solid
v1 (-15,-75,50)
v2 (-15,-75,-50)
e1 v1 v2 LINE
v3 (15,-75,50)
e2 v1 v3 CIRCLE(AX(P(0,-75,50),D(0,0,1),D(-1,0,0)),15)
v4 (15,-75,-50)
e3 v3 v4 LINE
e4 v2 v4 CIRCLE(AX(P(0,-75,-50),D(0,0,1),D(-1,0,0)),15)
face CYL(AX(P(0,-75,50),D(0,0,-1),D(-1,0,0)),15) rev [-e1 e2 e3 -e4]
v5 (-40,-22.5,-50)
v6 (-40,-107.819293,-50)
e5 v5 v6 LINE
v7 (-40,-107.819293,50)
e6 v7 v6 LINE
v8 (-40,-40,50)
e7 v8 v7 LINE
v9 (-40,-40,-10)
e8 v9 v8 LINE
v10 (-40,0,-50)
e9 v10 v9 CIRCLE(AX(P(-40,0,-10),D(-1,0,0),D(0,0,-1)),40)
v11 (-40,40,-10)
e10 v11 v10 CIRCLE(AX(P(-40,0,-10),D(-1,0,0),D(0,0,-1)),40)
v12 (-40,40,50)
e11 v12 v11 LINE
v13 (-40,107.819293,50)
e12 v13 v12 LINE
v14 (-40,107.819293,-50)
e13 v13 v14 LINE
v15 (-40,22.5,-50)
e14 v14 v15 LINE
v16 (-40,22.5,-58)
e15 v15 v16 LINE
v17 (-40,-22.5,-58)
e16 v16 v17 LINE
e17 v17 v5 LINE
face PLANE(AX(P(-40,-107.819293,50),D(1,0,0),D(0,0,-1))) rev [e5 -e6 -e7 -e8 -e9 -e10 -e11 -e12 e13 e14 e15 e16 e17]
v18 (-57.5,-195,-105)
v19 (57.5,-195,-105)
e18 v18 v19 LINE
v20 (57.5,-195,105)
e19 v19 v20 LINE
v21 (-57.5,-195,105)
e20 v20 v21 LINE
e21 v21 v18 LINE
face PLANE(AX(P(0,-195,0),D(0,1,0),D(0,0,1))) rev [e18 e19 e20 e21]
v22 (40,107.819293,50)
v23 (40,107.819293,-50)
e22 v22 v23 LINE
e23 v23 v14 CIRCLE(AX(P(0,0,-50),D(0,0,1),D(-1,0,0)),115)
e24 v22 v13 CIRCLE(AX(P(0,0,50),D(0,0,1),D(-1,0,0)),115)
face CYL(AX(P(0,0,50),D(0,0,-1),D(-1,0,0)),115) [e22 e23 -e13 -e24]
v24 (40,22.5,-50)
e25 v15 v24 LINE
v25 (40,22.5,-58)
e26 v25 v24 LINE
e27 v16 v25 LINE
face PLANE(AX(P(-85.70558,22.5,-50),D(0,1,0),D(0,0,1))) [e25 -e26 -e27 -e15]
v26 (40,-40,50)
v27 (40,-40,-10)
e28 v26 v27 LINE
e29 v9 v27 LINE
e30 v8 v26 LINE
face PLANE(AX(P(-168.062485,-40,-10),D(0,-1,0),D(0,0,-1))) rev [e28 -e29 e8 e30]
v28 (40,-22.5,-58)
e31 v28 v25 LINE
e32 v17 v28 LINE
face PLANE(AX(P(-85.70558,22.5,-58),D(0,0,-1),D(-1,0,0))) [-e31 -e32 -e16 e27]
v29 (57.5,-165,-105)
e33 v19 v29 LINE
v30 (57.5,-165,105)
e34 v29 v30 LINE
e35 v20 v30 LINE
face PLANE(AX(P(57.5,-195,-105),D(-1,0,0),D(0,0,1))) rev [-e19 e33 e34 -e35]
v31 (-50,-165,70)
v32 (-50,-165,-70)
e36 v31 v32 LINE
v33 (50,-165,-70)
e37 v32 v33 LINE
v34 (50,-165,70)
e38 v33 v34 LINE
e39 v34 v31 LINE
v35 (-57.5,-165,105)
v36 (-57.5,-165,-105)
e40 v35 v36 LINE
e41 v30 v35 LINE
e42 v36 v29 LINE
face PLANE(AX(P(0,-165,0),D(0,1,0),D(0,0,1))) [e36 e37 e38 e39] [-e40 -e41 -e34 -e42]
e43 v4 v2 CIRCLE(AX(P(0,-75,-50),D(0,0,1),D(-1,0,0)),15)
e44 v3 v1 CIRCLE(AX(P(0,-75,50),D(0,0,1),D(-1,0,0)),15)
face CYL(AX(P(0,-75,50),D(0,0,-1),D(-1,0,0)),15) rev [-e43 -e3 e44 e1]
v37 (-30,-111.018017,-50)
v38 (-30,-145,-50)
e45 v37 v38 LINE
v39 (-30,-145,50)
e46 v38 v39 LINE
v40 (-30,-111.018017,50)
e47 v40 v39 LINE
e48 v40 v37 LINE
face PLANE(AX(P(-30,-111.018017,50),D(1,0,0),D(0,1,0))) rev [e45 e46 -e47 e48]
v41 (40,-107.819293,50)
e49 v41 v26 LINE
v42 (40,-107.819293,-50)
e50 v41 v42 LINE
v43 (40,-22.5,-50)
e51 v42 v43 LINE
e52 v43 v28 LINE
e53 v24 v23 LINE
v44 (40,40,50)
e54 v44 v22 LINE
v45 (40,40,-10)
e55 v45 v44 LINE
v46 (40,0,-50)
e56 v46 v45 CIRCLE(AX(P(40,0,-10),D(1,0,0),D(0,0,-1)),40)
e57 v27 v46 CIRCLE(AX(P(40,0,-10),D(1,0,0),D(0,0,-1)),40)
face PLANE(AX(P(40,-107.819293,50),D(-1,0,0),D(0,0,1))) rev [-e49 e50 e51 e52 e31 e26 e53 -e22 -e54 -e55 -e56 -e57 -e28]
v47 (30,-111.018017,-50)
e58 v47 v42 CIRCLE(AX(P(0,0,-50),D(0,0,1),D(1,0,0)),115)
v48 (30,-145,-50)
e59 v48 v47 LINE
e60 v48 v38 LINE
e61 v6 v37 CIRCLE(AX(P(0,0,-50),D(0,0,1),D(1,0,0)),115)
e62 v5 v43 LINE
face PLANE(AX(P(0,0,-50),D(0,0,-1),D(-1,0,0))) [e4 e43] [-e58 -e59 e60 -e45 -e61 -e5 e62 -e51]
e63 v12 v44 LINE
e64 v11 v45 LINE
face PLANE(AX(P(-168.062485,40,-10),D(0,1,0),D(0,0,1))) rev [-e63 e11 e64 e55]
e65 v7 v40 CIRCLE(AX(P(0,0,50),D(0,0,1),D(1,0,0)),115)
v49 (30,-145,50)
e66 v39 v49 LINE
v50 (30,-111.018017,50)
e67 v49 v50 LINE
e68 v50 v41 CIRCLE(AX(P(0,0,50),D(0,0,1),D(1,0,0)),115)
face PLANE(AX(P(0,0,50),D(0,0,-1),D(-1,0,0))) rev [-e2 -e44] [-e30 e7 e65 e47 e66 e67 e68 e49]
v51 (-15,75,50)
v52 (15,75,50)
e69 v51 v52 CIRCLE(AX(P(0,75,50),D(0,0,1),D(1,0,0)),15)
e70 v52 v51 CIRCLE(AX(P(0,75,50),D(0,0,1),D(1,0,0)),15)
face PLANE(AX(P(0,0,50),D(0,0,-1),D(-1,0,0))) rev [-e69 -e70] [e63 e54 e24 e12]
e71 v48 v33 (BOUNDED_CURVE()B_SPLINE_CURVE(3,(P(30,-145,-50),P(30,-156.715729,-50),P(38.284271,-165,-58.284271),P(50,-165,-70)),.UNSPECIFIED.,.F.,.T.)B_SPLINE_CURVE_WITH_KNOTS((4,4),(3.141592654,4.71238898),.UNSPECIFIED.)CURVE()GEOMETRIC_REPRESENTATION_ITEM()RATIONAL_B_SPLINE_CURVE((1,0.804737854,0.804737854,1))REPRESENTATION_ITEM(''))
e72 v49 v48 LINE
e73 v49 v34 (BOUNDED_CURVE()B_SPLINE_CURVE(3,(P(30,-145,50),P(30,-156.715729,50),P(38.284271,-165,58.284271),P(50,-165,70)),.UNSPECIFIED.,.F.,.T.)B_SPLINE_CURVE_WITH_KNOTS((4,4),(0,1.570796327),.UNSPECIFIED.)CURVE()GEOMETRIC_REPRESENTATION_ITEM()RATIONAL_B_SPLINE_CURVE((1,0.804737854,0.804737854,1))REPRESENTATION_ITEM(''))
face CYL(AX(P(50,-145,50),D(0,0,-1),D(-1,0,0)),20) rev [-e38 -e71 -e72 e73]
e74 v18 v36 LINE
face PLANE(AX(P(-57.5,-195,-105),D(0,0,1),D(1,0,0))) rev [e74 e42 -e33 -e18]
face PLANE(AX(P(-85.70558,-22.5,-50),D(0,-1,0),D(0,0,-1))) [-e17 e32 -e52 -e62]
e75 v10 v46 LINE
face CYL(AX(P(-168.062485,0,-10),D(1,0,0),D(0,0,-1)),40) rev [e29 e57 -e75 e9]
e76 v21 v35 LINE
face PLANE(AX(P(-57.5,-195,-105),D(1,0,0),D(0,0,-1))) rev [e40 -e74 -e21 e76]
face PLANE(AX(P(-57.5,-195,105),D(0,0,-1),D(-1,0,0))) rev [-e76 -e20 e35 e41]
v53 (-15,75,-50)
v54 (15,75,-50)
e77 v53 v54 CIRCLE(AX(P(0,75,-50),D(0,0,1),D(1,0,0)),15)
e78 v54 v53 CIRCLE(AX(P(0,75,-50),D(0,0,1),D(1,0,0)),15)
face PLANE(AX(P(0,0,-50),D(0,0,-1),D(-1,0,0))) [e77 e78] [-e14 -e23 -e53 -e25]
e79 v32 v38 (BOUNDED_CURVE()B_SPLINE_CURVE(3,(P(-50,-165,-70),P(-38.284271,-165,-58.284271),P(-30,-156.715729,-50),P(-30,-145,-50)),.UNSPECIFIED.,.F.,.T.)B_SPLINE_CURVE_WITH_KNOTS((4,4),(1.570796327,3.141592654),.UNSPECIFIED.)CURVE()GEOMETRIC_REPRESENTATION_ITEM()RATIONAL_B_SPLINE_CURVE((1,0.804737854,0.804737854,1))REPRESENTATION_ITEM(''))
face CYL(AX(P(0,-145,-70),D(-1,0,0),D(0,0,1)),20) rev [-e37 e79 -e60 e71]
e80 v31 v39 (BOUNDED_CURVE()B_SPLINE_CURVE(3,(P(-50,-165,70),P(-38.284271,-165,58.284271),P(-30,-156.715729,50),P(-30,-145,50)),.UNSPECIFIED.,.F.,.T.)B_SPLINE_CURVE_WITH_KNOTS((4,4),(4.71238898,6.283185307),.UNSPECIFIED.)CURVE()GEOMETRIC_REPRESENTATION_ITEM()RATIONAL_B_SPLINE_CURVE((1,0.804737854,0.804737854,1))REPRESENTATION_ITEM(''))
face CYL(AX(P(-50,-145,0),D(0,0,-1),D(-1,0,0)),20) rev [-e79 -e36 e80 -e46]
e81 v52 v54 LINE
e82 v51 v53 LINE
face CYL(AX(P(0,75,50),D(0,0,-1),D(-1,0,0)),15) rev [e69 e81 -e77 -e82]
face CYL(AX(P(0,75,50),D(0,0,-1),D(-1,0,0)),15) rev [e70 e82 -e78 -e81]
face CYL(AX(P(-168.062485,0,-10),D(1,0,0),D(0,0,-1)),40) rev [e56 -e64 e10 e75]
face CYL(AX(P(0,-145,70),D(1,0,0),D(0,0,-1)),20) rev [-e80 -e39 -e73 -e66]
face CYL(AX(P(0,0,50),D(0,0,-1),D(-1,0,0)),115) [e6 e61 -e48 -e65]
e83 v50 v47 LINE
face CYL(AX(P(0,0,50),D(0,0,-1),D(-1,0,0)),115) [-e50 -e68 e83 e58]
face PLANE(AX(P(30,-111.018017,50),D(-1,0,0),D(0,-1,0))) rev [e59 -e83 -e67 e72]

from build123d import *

# Parameters (mm, degrees)
UPRIGHT_PROFILE_SKETCH_R    = 15
UPRIGHT_BODY_DEPTH          = 50
BASE_PLATE_SKETCH_W         = 115
BASE_PLATE_SKETCH_H         = 210
BASE_PLATE_210X115X30_DEPTH = 30
BASE_BLEND_FILLET_R20_R     = 20
SIDE_BOSS_SKETCH_W          = 8
SIDE_BOSS_SKETCH_H          = 45
SIDE_BOSS_DEPTH             = 80
UPRIGHT_PROFILE_CUT_DEPTH   = 80


with BuildPart() as part:
    # Upright Profile Sketch → Upright Body (new, symmetric)
    with BuildSketch(Plane.XY):
        with BuildLine():
            Line((-40, -107.819293264), (-40, 107.819293264))
            ThreePointArc((-40, 107.819293264), (0, 115), (40, 107.819293264))
            Line((40, 107.819293264), (40, -107.819293264))
            ThreePointArc((40, -107.819293264), (35.036523196, -109.532835453), (30, -111.018016556))
            Line((30, -111.018016556), (30, -165))
            Line((30, -165), (-30, -165))
            Line((-30, -165), (-30, -111.018016556))
            ThreePointArc((-30, -111.018016556), (-35.036523196, -109.532835453), (-40, -107.819293264))
        make_face()
        with Locations((0, 75)):
            Circle(UPRIGHT_PROFILE_SKETCH_R, mode=Mode.SUBTRACT)
        with Locations(Location((0, -75, 0), (0, 0, 180))):
            Circle(UPRIGHT_PROFILE_SKETCH_R, mode=Mode.SUBTRACT)
    extrude(amount=UPRIGHT_BODY_DEPTH, both=True)

    # Base Plate Sketch → Base Plate 210x115x30 (add)
    with BuildSketch(Plane.XZ.offset(165)):
        Rectangle(BASE_PLATE_SKETCH_W, BASE_PLATE_SKETCH_H)
    extrude(amount=BASE_PLATE_210X115X30_DEPTH)

    # Base Blend Fillet R20
    base_blend_fillet_r20_edges = [part.edges().sort_by_distance(p)[0] for p in [
        (30, -165, 0),
        (-30, -165, 0),
        (0, -165, 50),
        (0, -165, -50),
    ]]
    fillet(base_blend_fillet_r20_edges, radius=BASE_BLEND_FILLET_R20_R)

    # Side Boss Sketch → Side Boss (add)
    with BuildSketch(Plane(origin=(40, 0, 0), x_dir=(0, 0, -1), z_dir=(1, 0, 0))):
        with Locations((54, 0)):
            Rectangle(SIDE_BOSS_SKETCH_W, SIDE_BOSS_SKETCH_H)
    extrude(amount=-SIDE_BOSS_DEPTH)

    # Upright Cut Sketch → Upright Profile Cut (cut)
    with BuildSketch(Plane(origin=(40, 0, 0), x_dir=(0, 0, -1), z_dir=(1, 0, 0))):
        with BuildLine():
            Line((10, 40), (-50, 40))
            Line((-50, 40), (-50, -40))
            Line((-50, -40), (10, -40))
            ThreePointArc((10, -40), (50, 0), (10, 40))
        make_face()
    extrude(amount=-UPRIGHT_PROFILE_CUT_DEPTH, mode=Mode.SUBTRACT)


solid = part.part
